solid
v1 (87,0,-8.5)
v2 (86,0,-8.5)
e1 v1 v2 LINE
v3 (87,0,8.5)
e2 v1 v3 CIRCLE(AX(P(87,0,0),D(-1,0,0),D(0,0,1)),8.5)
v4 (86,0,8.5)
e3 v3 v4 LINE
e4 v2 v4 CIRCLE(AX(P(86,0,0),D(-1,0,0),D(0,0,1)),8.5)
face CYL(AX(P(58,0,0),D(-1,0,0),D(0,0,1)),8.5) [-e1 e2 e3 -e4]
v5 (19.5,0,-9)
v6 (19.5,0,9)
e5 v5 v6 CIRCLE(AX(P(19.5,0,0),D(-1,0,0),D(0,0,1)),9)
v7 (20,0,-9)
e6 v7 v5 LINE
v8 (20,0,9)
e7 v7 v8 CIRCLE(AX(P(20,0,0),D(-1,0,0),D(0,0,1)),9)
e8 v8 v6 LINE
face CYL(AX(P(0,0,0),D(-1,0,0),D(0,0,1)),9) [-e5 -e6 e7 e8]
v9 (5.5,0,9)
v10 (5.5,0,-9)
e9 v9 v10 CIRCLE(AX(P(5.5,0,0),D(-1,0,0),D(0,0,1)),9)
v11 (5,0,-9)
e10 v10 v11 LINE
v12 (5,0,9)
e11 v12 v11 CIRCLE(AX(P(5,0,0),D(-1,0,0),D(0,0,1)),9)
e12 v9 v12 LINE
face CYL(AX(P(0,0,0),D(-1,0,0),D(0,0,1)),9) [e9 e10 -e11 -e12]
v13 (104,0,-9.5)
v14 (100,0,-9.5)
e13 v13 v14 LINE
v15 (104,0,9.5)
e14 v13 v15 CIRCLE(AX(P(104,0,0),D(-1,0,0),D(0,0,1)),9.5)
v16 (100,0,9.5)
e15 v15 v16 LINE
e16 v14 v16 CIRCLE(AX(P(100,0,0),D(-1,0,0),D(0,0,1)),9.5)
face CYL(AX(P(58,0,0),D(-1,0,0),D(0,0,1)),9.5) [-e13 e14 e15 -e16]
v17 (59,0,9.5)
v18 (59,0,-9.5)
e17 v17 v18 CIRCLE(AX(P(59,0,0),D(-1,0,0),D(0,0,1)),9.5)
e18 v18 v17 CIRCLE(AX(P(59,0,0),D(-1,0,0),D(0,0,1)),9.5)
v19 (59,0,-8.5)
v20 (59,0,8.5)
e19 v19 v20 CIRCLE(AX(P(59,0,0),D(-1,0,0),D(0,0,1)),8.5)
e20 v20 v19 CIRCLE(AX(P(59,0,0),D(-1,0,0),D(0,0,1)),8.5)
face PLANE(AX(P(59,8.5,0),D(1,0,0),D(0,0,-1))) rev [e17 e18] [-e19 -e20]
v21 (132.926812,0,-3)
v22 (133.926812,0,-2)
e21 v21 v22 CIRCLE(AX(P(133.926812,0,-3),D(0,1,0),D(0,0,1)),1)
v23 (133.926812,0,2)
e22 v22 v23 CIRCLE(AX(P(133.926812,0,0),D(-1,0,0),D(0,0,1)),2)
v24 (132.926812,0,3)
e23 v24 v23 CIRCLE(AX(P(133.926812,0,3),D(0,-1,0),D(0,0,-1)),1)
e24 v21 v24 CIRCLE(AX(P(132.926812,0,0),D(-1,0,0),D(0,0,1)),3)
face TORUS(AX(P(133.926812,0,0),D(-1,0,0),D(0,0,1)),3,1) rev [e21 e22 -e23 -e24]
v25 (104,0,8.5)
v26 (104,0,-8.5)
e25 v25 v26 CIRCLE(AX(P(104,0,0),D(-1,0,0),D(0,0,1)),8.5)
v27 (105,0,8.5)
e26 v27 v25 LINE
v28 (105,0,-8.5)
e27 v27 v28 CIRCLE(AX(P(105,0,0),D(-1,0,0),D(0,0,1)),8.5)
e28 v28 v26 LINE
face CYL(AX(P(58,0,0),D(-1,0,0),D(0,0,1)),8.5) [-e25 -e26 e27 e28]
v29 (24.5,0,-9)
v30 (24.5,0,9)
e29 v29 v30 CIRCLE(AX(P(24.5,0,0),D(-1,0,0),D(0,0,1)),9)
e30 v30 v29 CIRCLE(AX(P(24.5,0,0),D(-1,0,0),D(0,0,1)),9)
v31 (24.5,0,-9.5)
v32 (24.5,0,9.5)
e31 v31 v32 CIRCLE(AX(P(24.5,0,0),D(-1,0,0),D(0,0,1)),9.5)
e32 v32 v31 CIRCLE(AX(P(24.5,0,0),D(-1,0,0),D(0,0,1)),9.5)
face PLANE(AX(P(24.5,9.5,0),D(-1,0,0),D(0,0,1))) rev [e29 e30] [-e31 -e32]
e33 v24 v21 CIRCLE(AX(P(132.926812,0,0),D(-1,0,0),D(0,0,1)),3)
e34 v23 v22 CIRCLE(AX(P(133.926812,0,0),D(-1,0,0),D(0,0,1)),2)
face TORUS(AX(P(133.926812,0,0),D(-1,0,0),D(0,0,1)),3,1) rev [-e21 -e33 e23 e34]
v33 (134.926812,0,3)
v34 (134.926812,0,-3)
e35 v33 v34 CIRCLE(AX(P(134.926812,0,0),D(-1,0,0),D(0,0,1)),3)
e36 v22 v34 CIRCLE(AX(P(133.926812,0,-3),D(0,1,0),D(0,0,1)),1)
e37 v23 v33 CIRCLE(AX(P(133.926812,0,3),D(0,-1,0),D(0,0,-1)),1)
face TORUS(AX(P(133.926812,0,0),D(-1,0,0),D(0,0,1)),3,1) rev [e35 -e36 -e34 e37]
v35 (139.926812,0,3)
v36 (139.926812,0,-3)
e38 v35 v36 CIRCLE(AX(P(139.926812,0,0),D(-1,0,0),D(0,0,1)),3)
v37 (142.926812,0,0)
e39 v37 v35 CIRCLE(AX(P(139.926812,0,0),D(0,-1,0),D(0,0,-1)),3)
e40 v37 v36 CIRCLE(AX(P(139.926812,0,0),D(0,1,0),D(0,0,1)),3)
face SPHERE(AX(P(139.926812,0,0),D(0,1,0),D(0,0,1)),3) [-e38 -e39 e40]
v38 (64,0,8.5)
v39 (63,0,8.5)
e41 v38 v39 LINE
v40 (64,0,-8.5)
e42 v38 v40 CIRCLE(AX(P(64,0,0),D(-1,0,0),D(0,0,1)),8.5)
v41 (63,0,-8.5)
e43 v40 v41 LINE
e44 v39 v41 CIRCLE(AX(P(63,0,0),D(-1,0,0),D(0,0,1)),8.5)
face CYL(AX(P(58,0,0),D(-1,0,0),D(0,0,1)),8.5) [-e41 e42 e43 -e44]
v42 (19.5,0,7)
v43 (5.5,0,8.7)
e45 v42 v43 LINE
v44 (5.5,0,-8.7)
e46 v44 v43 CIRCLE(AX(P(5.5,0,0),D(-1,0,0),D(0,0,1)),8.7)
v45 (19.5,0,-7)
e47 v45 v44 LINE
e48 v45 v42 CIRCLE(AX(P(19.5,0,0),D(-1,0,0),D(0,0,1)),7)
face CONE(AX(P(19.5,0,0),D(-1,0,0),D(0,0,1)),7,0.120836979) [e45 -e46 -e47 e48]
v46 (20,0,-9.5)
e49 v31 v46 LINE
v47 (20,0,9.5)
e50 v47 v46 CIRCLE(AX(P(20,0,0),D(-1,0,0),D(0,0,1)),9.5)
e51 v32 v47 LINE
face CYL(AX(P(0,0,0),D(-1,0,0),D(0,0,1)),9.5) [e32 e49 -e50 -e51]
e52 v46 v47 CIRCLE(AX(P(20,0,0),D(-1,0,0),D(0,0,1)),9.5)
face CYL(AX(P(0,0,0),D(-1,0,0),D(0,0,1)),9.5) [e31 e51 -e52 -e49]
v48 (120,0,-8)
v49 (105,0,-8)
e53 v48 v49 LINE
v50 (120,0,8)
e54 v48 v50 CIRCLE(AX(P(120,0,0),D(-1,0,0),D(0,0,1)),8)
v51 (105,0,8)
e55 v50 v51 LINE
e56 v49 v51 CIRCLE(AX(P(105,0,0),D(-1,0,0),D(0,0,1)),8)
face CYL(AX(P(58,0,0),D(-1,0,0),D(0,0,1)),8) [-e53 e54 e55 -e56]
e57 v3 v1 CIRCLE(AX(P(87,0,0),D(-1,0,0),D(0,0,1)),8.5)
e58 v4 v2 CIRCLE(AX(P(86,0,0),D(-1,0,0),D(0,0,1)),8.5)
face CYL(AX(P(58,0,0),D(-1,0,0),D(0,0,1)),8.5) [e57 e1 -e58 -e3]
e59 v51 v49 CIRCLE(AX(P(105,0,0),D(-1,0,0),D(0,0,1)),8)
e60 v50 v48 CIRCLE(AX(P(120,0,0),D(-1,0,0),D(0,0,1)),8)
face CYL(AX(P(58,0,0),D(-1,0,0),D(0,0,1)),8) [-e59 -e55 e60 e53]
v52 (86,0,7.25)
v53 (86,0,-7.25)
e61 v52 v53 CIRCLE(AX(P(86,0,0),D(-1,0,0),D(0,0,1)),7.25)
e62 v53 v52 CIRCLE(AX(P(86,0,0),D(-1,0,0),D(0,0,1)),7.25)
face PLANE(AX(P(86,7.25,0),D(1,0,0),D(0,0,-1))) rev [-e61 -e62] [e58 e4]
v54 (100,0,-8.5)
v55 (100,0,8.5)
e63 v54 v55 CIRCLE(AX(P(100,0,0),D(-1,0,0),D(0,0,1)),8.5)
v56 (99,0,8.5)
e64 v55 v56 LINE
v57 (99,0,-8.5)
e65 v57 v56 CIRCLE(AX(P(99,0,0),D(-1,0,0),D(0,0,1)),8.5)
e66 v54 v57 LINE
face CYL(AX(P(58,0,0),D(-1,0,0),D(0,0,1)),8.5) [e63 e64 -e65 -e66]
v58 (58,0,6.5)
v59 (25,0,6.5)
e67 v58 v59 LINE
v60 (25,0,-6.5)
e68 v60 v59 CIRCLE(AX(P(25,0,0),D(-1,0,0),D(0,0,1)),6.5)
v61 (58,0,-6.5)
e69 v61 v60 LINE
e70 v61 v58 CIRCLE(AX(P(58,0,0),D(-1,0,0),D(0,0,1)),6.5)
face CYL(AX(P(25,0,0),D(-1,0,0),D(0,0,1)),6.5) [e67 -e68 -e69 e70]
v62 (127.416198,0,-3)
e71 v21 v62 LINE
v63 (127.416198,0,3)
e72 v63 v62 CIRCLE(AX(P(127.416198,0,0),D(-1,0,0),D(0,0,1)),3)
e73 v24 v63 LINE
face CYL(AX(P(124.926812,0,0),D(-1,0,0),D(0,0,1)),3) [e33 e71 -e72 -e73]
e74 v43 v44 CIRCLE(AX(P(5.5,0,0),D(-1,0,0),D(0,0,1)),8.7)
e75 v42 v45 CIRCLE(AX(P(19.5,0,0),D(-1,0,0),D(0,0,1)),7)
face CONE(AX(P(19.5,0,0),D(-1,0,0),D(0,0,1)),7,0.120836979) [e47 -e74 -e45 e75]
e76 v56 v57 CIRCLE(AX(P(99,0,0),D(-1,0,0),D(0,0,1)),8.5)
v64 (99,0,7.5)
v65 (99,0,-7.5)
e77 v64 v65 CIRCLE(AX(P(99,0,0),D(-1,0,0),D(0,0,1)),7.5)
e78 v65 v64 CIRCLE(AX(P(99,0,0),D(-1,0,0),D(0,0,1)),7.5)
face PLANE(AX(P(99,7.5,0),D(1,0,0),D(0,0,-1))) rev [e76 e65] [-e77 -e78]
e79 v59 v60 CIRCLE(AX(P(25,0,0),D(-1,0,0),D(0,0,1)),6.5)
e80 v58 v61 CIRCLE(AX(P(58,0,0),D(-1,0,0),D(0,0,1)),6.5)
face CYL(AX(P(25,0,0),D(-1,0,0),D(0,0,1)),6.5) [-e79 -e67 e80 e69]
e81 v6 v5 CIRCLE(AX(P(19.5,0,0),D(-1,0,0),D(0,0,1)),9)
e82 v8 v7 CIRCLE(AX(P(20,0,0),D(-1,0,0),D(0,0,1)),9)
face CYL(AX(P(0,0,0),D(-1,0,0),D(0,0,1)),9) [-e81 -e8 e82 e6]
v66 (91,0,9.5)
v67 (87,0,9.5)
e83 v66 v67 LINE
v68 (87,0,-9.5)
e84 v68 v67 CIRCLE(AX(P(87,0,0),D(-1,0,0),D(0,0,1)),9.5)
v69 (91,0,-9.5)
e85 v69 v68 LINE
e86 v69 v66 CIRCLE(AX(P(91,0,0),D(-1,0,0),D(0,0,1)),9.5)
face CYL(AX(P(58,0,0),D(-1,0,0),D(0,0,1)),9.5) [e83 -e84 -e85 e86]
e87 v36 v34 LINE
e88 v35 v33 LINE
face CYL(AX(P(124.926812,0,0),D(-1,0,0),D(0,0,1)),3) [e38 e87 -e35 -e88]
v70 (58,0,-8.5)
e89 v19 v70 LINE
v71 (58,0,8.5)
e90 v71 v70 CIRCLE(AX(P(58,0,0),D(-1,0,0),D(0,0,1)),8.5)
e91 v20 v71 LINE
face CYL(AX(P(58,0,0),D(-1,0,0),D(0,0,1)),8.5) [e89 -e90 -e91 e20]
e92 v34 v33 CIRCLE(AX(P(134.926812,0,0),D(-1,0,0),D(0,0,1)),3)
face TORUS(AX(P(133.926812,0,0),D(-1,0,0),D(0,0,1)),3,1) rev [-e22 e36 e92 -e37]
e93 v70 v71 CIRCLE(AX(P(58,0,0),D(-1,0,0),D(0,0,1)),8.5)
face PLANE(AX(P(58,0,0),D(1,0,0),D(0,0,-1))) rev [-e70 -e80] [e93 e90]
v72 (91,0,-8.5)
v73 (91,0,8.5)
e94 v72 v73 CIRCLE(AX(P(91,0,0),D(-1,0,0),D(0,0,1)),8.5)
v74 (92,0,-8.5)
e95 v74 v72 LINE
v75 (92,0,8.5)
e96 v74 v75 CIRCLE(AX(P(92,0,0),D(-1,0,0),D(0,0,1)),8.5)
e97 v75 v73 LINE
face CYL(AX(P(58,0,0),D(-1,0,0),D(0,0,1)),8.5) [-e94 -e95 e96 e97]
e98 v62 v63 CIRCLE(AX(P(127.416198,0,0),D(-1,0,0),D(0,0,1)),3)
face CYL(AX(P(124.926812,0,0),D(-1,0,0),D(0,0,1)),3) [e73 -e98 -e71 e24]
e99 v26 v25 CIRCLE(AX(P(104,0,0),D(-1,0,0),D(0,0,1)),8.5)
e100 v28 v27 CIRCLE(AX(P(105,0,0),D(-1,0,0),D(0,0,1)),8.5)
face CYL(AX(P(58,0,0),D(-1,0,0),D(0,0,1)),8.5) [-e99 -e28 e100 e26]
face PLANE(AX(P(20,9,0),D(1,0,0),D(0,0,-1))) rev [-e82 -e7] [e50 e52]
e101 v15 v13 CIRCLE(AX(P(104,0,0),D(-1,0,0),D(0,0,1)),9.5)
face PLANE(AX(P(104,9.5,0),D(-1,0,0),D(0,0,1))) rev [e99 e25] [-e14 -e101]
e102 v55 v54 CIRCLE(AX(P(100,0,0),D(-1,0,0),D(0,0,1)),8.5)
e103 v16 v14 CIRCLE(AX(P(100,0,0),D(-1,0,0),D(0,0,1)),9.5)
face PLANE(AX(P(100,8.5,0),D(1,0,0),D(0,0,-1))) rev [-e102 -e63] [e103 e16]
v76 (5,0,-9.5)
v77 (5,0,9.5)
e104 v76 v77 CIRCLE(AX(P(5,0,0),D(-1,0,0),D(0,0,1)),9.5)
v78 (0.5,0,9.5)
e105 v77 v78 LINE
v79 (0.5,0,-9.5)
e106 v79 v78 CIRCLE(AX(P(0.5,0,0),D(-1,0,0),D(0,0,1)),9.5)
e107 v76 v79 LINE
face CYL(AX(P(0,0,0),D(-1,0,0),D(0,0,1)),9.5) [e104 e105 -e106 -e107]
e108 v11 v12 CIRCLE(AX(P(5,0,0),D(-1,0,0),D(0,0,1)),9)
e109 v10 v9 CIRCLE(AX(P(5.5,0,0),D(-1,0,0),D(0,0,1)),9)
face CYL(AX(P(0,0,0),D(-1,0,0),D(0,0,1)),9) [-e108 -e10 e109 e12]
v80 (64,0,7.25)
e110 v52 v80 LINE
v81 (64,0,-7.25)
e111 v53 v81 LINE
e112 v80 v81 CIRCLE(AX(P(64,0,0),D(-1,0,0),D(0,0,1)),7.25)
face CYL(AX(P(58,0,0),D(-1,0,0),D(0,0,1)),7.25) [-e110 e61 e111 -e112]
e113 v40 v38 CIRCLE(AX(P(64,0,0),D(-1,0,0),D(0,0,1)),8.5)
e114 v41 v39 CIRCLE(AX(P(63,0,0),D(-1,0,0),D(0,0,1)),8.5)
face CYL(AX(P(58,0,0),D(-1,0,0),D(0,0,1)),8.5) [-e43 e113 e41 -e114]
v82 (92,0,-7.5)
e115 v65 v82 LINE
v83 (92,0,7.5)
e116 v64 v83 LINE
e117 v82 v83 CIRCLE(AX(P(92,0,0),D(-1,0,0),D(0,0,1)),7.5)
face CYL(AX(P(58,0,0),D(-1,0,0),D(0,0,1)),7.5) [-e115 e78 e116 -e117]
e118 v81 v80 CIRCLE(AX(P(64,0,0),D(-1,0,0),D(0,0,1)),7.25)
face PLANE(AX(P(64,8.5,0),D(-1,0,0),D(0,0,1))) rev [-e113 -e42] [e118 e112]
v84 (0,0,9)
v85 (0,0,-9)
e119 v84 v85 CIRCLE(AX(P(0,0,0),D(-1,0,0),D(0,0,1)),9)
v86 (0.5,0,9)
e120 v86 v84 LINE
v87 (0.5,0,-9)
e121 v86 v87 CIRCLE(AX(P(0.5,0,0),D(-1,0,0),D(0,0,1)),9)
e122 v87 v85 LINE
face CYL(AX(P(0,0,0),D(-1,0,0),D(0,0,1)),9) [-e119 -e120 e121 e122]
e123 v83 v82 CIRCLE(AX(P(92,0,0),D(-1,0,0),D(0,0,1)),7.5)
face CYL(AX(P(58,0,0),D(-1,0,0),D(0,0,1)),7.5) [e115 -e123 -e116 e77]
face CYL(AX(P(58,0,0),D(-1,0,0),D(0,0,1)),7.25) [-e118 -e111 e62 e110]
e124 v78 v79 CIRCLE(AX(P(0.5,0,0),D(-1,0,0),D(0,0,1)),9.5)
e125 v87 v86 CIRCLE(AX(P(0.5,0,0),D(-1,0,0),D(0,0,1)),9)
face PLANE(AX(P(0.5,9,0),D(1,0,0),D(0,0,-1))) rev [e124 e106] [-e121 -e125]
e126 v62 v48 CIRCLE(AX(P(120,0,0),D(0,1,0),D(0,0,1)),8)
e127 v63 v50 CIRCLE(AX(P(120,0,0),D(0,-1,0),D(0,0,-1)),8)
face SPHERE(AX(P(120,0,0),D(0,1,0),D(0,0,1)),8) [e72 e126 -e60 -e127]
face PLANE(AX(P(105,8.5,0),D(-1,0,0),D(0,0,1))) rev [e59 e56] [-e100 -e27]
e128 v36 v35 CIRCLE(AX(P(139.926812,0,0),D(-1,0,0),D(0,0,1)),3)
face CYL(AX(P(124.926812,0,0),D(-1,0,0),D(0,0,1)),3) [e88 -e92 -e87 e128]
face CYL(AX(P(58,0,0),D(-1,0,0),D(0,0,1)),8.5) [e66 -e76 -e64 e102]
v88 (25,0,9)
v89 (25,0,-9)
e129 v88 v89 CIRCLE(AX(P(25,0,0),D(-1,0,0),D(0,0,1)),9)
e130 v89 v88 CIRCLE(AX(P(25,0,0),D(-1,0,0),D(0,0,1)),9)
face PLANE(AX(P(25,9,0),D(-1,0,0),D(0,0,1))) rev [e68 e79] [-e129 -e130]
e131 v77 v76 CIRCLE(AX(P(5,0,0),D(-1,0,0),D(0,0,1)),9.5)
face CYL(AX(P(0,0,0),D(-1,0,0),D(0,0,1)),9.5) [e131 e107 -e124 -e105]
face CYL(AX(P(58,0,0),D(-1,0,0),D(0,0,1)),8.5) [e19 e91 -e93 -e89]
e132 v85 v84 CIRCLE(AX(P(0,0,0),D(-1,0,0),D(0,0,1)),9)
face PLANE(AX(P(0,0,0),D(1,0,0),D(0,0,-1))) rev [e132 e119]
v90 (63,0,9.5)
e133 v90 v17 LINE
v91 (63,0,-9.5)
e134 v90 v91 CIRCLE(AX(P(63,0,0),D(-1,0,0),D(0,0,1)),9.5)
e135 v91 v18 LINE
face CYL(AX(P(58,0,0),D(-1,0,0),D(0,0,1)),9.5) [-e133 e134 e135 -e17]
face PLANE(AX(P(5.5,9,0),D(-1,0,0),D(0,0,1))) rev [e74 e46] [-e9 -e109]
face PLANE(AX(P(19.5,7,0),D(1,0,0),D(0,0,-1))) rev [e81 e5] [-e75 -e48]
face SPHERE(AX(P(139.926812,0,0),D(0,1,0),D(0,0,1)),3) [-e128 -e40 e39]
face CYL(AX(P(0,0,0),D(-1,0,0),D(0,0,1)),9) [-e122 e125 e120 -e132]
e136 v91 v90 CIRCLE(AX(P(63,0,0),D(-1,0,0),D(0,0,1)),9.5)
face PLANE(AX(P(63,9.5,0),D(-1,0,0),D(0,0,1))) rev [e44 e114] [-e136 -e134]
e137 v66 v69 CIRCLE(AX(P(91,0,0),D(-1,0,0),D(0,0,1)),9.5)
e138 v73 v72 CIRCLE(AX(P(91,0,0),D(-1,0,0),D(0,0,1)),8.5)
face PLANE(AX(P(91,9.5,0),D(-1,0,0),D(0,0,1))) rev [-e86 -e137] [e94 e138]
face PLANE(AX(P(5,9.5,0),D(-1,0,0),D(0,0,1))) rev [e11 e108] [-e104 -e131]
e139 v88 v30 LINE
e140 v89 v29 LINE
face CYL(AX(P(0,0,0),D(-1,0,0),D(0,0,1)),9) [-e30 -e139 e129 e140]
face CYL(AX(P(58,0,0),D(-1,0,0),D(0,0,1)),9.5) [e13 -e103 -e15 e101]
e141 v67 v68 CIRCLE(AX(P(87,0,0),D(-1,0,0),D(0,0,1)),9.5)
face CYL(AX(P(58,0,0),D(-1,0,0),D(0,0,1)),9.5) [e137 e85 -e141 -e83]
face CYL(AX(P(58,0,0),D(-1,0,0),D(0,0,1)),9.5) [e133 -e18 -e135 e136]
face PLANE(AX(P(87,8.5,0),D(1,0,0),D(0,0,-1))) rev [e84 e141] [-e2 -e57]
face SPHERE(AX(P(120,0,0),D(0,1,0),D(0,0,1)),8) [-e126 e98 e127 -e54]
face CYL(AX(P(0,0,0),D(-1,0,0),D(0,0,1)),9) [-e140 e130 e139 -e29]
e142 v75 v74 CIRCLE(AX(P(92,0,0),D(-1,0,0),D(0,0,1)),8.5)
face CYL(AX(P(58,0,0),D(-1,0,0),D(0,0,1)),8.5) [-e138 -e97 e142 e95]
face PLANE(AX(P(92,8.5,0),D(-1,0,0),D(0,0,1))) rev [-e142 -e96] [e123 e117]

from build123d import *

# Parameters (mm, degrees)
MID_SECTION_PROFILE_W = 33
MID_SECTION_PROFILE_H = 6.5
TIP_DOME_FILLET_R8_R  = 8
END_FLARE_FILLET_R3_R = 3


with BuildPart() as part:
    # Shaft Core Profile → Shaft Core Revolve (revolve)
    with BuildSketch(Plane.XY, mode=Mode.PRIVATE) as shaft_core_revolve_sk:
        Polygon((0, 0), (0, 9), (0.5, 9), (0.5, 9.5), (5, 9.5), (5, 9), (5.5, 9), (5.5, 8.7), (19.5, 7), (19.5, 9), (20, 9), (20, 9.5), (24.5, 9.5), (24.5, 9), (25, 9), (25, 0), align=None)
    revolve(shaft_core_revolve_sk.sketch.rotate(Axis((0, 0, 0), (1, 0, 0)), 90), axis=Axis((0, 0, 0), (1, 0, 0)))

    # Mid Section Profile → Mid Section Revolve (revolve)
    with BuildSketch(Plane.XY, mode=Mode.PRIVATE) as mid_section_revolve_sk:
        with Locations((41.5, 3.25)):
            Rectangle(MID_SECTION_PROFILE_W, MID_SECTION_PROFILE_H)
    revolve(mid_section_revolve_sk.sketch.rotate(Axis((25, 0, 0), (1, 0, 0)), 90), axis=Axis((25, 0, 0), (1, 0, 0)))

    # Collars Profile → Collars Revolve (revolve)
    with BuildSketch(Plane.XY, mode=Mode.PRIVATE) as collars_revolve_sk:
        Polygon((58, 0), (58, 8.5), (59, 8.5), (59, 9.5), (63, 9.5), (63, 8.5), (64, 8.5), (64, 7.25), (86, 7.25), (86, 8.5), (87, 8.5), (87, 9.5), (91, 9.5), (91, 8.5), (92, 8.5), (92, 7.5), (99, 7.5), (99, 8.5), (100, 8.5), (100, 9.5), (104, 9.5), (104, 8.5), (105, 8.5), (105, 8), (120, 8), (128, 8), (128, 0), align=None)
    revolve(collars_revolve_sk.sketch.rotate(Axis((58, 0, 0), (1, 0, 0)), 90), axis=Axis((58, 0, 0), (1, 0, 0)))

    # Tip Dome Fillet R8
    tip_dome_fillet_r8_edges = [part.edges().sort_by_distance(p)[0] for p in [
        (128, 0, -8),
    ]]
    fillet(tip_dome_fillet_r8_edges, radius=TIP_DOME_FILLET_R8_R)

    # End Flare Profile → End Flare Revolve (revolve)
    with BuildSketch(Plane.XY, mode=Mode.PRIVATE) as end_flare_revolve_sk:
        with BuildLine():
            Line((124.926812112, 0), (124.926812112, 3))
            Line((124.926812112, 3), (132.926812112, 3))
            ThreePointArc((132.926812112, 3), (133.926812112, 2), (134.926812112, 3))
            Line((134.926812112, 3), (139.926812112, 3))
            Line((139.926812112, 3), (142.926812112, 3))
            Line((142.926812112, 3), (142.926812112, 0))
            Line((142.926812112, 0), (124.926812112, 0))
        make_face()
    revolve(end_flare_revolve_sk.sketch.rotate(Axis((124.926812112, 0, 0), (1, 0, 0)), 90), axis=Axis((124.926812112, 0, 0), (1, 0, 0)))

    # End Flare Fillet R3
    end_flare_fillet_r3_edges = [part.edges().sort_by_distance(p)[0] for p in [
        (142.926812112, 0, -3),
    ]]
    fillet(end_flare_fillet_r3_edges, radius=END_FLARE_FILLET_R3_R)


solid = part.part
